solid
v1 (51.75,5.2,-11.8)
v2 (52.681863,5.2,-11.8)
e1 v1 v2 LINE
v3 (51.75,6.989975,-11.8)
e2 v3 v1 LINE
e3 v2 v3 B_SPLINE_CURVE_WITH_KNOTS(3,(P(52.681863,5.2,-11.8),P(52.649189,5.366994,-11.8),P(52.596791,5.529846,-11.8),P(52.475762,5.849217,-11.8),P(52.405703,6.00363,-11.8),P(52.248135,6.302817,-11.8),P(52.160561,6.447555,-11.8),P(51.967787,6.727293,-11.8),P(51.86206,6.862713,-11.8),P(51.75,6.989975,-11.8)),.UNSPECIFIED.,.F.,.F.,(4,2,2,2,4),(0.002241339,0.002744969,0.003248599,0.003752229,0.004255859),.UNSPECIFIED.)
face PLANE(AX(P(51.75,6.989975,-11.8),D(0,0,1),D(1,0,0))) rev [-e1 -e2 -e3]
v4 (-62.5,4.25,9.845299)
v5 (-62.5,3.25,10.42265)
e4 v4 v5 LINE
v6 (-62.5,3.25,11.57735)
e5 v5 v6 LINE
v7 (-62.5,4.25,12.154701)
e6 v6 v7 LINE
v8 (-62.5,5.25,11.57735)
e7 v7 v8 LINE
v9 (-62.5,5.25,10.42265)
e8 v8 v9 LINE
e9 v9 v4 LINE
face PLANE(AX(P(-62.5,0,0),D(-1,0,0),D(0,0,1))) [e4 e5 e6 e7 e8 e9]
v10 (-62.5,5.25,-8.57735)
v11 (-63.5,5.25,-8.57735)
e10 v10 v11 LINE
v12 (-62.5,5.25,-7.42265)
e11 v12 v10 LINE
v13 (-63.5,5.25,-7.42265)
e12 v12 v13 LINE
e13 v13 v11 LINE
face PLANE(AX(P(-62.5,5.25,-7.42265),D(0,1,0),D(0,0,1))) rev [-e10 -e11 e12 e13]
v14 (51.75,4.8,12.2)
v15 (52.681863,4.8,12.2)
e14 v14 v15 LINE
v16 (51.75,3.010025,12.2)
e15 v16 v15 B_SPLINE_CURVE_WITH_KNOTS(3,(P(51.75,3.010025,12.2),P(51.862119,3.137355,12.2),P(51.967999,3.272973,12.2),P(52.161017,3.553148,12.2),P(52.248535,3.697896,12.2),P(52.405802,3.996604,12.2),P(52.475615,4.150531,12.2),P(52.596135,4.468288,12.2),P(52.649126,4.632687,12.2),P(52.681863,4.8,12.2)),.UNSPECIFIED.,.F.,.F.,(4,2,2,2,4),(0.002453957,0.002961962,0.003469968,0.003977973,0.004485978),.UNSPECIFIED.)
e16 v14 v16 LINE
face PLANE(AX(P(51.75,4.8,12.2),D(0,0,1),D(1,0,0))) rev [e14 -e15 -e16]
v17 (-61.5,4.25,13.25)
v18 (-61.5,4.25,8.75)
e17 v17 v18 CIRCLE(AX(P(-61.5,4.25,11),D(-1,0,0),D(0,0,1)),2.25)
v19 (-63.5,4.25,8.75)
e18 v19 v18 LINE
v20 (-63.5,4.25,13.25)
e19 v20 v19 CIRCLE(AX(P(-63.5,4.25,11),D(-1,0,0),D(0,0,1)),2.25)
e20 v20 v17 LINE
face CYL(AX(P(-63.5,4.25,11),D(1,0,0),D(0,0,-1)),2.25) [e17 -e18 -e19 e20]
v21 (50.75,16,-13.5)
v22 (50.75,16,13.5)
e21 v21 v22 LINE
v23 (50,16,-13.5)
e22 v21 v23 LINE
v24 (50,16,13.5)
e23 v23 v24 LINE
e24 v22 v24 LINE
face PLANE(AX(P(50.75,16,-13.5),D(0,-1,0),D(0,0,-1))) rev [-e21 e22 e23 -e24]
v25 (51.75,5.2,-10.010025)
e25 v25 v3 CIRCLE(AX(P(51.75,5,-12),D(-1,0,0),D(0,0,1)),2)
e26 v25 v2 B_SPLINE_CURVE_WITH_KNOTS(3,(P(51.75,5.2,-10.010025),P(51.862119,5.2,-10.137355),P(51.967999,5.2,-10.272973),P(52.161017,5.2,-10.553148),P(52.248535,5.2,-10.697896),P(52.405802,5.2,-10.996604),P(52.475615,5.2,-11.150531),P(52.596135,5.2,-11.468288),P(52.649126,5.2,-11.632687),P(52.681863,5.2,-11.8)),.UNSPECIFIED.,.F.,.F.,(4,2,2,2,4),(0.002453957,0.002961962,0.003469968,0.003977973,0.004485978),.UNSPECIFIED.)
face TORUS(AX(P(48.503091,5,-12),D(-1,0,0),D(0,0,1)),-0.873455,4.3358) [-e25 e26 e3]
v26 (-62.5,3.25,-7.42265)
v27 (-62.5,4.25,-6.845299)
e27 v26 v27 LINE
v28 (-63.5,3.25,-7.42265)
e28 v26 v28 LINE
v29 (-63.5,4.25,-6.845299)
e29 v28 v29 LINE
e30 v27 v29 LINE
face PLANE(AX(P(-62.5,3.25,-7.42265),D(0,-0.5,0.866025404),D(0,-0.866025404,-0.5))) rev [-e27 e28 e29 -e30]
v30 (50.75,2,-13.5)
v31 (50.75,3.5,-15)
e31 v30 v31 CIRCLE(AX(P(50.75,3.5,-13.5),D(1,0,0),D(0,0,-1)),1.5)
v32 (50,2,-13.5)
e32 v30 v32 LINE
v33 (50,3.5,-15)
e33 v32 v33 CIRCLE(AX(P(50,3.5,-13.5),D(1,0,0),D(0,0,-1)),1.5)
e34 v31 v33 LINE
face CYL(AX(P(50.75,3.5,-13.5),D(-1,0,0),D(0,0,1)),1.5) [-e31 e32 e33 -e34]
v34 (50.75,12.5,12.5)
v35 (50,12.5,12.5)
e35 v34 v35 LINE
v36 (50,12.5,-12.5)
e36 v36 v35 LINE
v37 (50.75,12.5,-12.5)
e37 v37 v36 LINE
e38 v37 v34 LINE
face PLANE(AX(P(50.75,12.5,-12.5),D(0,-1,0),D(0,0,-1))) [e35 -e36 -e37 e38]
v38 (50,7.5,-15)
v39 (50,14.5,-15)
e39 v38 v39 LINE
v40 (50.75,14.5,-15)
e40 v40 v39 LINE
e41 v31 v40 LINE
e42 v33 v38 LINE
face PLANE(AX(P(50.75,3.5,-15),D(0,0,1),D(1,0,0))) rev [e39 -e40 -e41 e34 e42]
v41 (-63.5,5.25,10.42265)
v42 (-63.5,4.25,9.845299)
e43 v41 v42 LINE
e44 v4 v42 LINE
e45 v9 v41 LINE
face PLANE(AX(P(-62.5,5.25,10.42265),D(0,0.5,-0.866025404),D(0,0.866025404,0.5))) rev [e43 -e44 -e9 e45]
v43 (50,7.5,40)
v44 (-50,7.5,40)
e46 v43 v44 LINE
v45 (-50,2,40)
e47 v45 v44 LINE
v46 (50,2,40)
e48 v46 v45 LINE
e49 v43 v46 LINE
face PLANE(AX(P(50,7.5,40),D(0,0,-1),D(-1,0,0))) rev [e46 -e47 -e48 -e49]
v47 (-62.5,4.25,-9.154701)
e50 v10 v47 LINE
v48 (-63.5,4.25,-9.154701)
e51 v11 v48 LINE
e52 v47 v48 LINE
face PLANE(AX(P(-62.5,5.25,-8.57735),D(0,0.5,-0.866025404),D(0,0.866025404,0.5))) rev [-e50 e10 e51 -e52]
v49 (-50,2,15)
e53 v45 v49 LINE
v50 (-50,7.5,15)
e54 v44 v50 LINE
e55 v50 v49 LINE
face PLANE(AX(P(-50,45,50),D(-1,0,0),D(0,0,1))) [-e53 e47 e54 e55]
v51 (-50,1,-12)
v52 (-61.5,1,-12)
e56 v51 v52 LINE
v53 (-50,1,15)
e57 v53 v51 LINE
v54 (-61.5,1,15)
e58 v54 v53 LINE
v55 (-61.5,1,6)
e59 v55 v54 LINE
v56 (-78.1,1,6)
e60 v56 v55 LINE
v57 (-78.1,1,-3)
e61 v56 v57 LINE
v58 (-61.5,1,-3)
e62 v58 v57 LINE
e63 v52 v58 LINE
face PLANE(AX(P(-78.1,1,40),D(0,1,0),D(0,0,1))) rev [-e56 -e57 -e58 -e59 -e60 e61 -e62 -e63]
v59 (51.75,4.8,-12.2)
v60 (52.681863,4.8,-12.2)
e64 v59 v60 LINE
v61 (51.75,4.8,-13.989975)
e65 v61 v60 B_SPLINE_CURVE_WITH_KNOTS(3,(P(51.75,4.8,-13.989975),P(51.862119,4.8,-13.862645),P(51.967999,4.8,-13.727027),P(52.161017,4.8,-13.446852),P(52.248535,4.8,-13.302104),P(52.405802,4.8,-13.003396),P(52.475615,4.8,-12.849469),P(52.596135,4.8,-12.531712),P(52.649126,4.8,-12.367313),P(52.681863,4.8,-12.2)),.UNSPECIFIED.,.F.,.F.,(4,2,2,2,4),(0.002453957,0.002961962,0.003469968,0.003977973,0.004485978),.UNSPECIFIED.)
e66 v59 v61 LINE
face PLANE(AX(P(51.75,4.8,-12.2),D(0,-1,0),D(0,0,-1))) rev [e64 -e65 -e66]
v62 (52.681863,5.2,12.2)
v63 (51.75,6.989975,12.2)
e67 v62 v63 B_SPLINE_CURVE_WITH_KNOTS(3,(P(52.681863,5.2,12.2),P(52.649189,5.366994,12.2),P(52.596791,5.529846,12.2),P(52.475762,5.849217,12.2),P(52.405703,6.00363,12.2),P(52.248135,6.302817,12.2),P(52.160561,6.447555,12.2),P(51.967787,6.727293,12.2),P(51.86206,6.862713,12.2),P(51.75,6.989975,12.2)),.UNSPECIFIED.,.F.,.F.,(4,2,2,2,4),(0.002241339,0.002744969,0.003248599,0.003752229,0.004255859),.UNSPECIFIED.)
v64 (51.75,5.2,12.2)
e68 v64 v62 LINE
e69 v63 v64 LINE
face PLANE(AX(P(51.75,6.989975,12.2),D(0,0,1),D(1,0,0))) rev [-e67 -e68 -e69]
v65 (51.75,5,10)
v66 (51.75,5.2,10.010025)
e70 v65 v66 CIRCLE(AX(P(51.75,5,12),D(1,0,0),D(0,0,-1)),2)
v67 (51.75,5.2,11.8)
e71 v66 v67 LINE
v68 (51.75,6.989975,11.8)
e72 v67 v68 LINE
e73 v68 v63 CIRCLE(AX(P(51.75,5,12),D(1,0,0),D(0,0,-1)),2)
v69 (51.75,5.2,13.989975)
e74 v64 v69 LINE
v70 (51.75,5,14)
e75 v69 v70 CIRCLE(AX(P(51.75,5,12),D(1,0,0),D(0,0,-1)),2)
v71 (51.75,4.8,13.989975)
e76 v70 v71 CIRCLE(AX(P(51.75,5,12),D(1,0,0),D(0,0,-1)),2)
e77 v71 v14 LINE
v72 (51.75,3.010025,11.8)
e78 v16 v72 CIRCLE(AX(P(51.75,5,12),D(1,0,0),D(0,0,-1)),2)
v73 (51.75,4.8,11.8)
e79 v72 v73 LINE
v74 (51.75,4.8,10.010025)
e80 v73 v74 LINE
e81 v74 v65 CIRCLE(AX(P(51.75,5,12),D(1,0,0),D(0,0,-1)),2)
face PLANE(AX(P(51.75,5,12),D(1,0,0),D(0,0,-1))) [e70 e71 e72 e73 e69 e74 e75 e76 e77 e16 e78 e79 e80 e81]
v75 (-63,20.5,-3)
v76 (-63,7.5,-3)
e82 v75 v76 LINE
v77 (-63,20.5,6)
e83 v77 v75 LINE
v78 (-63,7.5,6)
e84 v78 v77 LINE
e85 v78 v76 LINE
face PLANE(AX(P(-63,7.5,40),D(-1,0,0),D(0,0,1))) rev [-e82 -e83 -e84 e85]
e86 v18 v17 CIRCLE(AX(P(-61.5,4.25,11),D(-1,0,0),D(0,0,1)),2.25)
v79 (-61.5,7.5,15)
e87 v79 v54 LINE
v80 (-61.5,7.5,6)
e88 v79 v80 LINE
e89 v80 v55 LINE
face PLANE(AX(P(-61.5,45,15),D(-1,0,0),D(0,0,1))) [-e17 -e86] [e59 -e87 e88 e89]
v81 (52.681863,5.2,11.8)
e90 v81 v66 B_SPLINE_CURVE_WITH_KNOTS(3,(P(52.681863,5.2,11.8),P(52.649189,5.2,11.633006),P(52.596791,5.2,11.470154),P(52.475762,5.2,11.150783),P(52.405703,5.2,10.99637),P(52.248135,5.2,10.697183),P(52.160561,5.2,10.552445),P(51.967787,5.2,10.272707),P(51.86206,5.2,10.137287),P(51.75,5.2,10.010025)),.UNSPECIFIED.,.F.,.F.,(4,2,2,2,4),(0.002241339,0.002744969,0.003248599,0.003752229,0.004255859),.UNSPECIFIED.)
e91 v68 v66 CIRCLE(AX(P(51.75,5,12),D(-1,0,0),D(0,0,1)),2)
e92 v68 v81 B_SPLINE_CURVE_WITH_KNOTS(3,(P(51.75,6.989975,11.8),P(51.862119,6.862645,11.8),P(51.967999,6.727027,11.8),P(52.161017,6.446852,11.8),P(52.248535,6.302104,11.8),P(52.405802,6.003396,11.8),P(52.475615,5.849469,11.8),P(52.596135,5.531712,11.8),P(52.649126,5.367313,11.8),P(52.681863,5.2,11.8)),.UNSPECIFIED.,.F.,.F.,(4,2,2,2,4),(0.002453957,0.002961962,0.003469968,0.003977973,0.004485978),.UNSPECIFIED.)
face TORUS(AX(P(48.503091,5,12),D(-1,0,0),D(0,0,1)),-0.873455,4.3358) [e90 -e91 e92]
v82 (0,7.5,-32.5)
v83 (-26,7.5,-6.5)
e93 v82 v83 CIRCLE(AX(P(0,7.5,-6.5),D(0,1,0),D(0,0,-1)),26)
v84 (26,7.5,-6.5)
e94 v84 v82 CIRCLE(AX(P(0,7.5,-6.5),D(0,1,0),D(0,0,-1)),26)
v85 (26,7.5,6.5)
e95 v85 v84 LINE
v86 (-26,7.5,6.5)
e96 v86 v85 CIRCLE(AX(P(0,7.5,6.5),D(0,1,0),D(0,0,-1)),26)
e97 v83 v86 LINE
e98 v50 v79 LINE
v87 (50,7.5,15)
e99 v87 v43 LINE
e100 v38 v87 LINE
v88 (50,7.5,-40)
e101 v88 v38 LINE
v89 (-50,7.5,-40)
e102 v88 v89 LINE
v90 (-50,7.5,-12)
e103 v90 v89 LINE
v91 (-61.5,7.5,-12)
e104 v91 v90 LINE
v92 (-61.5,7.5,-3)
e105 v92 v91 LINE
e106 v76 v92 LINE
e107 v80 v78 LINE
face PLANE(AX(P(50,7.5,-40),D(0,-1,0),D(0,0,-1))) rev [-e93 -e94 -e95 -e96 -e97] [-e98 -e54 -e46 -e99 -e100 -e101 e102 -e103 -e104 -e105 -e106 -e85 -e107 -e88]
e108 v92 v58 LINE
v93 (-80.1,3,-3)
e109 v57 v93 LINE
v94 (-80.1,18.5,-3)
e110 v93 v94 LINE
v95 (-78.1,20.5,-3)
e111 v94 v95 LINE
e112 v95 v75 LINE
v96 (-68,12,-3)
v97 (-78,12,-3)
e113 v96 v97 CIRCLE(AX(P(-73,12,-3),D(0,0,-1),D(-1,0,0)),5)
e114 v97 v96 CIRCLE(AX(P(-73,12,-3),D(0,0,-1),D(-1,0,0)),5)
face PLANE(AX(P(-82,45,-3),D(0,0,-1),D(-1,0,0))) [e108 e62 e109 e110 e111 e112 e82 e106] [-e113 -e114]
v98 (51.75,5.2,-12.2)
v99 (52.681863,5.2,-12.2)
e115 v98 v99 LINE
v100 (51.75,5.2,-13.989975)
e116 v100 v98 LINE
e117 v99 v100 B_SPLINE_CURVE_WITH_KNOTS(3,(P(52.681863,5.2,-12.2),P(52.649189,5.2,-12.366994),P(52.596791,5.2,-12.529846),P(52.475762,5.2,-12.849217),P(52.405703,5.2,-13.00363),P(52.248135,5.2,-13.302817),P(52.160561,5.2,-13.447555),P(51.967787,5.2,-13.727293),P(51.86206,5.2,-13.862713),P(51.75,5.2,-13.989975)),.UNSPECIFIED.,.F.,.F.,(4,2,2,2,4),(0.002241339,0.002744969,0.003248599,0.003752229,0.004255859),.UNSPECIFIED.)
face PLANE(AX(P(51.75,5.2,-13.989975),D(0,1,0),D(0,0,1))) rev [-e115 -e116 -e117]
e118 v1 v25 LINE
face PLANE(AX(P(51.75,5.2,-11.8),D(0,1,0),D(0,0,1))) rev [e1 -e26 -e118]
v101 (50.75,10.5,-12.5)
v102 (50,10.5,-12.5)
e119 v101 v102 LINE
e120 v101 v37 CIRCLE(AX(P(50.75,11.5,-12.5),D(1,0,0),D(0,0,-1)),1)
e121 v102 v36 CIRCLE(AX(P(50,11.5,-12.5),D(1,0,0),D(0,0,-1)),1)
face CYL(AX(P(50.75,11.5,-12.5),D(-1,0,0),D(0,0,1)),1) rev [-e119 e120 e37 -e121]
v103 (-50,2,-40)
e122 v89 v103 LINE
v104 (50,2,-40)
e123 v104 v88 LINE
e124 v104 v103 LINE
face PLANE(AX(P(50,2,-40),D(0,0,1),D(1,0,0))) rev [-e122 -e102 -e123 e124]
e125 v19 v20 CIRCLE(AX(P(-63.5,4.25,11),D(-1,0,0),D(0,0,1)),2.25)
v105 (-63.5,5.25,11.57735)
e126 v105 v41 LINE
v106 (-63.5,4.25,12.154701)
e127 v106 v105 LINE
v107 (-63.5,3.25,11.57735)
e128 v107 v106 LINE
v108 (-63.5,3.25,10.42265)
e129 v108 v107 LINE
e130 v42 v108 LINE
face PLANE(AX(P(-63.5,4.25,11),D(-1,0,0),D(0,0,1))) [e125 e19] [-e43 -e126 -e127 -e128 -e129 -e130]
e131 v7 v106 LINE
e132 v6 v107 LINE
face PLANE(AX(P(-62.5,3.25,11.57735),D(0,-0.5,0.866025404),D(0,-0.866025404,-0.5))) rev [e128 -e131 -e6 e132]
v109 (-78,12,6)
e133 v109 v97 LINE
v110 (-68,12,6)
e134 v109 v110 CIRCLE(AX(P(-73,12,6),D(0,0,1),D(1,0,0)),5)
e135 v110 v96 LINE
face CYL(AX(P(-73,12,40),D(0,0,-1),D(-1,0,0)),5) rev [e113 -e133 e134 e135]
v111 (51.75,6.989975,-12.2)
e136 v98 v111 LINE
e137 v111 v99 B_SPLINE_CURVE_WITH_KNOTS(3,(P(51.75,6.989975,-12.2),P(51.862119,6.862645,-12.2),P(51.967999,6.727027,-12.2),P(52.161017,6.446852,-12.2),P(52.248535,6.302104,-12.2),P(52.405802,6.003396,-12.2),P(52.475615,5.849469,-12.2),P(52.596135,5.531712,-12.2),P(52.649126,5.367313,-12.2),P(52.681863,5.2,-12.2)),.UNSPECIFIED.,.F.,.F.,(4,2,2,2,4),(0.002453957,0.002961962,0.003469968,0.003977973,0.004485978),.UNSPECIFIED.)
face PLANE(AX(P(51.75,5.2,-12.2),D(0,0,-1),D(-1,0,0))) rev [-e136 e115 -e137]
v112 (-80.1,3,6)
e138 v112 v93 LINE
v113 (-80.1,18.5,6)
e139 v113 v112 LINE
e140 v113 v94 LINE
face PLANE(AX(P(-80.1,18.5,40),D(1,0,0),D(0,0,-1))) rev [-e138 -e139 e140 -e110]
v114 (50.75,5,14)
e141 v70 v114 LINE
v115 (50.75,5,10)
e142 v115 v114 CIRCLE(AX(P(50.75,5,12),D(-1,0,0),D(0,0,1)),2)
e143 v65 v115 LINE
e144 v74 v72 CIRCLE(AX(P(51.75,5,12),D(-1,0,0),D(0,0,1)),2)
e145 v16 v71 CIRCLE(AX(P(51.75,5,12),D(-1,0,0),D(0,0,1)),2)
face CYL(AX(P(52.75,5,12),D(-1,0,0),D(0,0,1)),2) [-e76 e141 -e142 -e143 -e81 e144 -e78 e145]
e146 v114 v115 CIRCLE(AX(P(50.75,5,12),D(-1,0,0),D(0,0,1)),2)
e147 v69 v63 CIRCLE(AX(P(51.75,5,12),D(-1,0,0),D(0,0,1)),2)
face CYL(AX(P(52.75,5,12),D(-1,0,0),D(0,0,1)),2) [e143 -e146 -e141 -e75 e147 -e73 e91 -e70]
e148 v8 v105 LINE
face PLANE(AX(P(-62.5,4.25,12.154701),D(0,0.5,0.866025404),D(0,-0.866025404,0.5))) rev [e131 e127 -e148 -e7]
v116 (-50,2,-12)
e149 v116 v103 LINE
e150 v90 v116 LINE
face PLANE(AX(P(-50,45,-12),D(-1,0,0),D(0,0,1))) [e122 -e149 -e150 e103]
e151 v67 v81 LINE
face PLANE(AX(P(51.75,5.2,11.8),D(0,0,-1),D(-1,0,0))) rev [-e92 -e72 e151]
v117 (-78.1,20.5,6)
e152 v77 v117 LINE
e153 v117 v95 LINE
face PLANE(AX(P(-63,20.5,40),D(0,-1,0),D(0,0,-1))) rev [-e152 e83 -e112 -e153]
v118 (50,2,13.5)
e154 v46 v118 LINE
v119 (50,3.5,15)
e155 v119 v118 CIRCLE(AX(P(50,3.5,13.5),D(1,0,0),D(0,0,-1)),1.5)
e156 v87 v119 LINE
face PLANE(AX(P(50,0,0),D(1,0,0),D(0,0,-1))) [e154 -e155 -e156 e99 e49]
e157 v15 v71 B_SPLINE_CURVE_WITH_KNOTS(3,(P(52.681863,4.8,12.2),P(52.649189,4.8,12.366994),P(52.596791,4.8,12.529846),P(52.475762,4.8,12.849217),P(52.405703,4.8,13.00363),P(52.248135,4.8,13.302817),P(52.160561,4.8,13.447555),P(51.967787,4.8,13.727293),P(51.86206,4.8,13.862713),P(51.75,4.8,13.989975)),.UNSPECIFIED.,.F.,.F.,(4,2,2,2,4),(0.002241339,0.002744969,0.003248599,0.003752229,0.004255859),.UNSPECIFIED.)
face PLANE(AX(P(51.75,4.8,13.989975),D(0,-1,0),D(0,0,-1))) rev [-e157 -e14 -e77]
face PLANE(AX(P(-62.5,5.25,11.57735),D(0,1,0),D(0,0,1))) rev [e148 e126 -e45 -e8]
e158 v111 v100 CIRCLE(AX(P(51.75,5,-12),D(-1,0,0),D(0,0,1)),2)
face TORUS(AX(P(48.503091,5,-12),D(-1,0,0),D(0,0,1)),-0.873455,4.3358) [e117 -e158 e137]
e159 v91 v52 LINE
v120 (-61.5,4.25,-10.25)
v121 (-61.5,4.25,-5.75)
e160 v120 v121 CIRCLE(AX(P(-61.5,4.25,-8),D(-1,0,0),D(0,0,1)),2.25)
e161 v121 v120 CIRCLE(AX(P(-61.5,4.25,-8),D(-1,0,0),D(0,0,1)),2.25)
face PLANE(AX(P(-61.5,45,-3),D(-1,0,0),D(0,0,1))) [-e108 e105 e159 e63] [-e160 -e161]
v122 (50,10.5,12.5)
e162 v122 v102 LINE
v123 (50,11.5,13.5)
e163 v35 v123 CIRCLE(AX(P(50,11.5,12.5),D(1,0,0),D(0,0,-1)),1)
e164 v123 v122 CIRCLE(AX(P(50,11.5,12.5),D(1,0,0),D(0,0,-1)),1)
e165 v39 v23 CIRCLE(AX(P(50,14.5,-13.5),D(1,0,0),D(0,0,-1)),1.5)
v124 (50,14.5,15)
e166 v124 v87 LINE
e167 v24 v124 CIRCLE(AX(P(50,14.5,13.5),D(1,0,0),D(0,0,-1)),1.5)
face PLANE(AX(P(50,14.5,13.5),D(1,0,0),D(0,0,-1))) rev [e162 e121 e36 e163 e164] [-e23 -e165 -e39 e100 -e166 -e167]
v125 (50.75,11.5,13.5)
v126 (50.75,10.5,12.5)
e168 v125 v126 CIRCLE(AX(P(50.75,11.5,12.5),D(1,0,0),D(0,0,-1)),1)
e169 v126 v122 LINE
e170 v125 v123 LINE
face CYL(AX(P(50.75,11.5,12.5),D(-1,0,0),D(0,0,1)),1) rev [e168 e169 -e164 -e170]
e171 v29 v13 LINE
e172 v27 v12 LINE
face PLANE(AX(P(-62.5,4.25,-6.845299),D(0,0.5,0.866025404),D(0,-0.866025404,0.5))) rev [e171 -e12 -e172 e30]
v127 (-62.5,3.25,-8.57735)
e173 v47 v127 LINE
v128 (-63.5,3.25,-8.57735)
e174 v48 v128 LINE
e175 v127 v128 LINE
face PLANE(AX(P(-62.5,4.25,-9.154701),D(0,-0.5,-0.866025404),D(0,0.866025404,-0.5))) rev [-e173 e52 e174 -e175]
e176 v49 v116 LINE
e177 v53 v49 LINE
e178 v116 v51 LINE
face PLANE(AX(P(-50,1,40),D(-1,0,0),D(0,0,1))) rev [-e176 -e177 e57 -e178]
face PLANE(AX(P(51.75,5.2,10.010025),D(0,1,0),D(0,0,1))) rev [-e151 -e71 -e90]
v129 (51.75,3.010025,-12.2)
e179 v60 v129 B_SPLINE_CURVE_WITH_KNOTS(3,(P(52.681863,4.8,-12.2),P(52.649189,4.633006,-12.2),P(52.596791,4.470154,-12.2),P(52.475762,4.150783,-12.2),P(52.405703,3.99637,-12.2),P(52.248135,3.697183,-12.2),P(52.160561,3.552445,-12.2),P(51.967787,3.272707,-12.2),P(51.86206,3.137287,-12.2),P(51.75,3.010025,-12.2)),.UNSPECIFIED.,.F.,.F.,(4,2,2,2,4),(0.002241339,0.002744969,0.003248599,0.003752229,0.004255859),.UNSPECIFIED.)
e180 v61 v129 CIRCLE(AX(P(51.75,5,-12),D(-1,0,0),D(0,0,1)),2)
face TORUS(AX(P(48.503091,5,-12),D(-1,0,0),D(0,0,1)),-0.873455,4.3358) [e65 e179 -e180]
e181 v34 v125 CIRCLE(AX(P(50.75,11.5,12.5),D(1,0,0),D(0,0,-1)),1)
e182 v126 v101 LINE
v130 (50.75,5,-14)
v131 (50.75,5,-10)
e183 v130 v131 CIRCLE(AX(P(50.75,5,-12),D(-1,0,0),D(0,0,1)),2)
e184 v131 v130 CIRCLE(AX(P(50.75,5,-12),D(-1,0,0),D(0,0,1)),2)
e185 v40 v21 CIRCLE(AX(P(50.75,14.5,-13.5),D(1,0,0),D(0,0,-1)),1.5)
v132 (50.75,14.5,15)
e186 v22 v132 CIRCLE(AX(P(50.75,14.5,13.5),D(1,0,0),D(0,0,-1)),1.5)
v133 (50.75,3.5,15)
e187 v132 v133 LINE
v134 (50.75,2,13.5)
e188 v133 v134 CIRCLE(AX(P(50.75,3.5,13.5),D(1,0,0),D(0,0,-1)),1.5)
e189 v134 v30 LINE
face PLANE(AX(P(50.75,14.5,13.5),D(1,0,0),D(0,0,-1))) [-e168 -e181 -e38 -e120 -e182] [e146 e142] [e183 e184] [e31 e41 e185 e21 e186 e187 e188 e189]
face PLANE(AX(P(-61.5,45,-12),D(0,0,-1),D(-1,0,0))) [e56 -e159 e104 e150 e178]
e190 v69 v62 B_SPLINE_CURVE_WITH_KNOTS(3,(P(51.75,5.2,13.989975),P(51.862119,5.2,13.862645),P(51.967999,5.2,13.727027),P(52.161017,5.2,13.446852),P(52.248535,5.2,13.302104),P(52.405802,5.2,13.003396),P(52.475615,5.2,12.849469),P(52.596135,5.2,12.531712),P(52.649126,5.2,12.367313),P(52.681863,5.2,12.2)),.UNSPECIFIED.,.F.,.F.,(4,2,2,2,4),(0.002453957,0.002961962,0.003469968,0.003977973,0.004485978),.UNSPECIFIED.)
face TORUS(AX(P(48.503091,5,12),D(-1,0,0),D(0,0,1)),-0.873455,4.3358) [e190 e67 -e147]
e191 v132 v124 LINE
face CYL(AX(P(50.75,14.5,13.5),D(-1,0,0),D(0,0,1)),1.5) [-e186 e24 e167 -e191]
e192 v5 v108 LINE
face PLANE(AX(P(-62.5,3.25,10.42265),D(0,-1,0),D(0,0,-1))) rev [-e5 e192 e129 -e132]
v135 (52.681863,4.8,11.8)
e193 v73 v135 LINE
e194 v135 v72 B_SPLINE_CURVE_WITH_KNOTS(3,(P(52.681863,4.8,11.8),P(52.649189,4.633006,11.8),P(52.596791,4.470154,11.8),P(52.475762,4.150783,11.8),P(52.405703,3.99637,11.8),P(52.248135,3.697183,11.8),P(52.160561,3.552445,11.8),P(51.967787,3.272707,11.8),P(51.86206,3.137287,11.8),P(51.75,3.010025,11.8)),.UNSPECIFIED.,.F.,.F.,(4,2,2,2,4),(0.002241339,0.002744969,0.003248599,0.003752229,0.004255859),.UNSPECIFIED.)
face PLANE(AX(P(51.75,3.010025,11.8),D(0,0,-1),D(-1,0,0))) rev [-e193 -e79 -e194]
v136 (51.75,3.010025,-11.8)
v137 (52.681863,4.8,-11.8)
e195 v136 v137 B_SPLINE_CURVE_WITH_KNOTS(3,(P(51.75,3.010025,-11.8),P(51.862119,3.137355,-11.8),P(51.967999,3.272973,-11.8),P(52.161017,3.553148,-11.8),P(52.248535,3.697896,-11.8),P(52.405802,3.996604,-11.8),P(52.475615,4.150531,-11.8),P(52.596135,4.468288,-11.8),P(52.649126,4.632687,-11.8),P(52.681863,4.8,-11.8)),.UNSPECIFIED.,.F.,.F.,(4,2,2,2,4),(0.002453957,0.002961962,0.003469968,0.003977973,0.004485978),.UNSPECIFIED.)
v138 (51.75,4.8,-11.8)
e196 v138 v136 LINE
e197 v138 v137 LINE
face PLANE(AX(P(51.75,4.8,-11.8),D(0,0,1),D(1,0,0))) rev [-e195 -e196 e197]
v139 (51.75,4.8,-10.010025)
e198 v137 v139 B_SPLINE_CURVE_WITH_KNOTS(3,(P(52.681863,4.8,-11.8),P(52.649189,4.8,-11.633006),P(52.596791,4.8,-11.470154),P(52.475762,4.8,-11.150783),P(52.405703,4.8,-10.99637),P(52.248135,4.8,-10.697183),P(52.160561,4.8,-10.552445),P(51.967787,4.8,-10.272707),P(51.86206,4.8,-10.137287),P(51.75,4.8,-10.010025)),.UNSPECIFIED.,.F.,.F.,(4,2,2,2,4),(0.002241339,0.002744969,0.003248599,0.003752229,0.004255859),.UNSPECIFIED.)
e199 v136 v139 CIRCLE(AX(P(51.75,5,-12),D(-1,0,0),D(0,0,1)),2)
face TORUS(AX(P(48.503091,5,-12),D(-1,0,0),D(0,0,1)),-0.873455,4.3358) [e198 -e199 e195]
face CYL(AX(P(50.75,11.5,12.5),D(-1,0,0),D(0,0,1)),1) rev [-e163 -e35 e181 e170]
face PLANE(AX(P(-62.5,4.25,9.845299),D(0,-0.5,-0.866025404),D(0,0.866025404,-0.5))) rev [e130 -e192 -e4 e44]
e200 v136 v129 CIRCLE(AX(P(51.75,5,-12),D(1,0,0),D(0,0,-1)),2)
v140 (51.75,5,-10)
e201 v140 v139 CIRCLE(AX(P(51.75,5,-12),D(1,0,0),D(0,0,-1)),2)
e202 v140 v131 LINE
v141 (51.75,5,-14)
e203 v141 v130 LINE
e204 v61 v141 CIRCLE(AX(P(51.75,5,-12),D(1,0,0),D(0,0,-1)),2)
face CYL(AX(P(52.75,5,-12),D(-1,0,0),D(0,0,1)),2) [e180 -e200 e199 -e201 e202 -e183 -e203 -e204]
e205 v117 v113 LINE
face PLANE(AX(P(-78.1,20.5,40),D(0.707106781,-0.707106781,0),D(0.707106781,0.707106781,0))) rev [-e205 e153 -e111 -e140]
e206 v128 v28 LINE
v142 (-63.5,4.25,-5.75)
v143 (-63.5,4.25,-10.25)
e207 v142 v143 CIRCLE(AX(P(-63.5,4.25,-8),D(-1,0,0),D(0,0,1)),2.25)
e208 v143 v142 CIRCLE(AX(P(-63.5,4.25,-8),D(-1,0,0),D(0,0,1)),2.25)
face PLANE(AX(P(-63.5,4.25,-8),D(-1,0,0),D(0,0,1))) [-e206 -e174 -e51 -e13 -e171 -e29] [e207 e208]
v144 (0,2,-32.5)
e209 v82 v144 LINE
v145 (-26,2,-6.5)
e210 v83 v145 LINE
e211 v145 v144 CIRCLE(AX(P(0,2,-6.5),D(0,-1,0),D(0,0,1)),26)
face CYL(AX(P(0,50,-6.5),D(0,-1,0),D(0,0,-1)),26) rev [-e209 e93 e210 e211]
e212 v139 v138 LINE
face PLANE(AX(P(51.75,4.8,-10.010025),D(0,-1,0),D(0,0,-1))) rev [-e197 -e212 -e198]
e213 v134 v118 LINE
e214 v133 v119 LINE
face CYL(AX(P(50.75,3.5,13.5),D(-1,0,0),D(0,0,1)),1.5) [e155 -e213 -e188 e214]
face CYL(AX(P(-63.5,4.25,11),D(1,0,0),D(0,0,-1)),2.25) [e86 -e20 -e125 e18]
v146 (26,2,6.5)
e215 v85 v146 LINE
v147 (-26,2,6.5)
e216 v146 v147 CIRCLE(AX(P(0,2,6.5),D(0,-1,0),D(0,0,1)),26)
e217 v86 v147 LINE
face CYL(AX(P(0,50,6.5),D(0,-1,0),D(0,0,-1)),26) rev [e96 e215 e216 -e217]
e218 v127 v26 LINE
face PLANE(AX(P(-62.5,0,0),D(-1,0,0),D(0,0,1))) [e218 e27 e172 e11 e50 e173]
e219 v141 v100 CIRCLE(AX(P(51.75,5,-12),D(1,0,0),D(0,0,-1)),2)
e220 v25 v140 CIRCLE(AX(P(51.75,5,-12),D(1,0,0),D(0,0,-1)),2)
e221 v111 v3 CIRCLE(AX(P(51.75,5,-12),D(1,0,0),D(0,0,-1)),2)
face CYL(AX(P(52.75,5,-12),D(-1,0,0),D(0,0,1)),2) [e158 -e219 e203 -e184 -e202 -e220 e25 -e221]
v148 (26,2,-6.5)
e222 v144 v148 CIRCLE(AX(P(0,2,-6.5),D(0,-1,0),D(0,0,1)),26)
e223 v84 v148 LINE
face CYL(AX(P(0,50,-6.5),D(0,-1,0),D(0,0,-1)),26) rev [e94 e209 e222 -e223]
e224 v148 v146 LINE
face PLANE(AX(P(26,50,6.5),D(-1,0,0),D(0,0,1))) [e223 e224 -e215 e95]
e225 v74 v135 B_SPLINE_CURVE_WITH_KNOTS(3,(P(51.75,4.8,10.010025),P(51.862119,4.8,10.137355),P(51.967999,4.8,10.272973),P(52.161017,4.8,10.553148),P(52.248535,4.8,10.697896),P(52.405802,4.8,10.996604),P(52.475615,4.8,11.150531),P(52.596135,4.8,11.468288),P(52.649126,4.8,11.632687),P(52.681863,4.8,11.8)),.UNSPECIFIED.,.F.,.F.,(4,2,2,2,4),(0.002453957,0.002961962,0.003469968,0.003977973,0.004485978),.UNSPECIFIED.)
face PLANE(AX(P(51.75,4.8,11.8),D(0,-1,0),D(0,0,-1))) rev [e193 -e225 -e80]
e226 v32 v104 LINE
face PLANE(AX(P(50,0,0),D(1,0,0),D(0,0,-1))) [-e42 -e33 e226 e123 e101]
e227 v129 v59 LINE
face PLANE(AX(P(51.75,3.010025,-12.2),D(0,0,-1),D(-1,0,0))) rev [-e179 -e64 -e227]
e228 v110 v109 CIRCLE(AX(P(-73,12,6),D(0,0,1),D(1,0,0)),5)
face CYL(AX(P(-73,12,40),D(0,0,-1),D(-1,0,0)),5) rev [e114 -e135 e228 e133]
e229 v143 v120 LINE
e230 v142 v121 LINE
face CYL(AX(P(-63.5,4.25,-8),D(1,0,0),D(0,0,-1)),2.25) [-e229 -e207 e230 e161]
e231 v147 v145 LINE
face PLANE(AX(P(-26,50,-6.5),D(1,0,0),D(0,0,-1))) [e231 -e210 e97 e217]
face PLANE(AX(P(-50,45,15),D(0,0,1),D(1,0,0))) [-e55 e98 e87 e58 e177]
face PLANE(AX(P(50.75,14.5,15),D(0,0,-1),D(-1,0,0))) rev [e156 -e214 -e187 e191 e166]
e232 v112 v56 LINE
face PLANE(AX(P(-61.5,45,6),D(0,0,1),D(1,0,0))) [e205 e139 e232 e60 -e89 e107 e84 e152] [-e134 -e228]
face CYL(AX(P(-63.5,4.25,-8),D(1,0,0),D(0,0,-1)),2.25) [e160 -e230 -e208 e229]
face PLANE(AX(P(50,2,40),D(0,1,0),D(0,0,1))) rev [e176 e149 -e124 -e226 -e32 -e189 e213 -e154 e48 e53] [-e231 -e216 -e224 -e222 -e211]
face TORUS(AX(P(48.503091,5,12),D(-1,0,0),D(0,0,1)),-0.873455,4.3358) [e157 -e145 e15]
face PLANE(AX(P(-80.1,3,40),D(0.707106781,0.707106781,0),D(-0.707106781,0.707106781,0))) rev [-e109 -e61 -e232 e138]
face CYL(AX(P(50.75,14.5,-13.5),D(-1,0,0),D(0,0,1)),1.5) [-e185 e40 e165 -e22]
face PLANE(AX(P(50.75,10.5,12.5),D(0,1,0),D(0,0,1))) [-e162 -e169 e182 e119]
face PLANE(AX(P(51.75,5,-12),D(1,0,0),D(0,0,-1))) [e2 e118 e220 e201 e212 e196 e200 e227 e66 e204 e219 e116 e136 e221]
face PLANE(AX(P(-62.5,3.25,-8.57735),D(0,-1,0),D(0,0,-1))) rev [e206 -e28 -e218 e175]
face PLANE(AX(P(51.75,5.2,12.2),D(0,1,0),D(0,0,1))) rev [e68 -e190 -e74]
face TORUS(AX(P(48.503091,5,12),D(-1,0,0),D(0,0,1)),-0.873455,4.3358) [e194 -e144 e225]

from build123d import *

# Parameters (mm, degrees)
EXTRUDE_1_DEPTH      = 50
EXTRUDE_1_DEPTH_BACK = 50
SKETCH_1_W           = 80
SKETCH_1_H           = 5.5
EXTRUDE_2_DEPTH      = 40
EXTRUDE_2_DEPTH_BACK = 40
SKETCH_2_R           = 5
CUT_EXTRUDE_1_DEPTH  = 45
EXTRUDE_3_DEPTH      = 0.75
CUT_EXTRUDE_2_DEPTH  = 1
CUT_EXTRUDE_3_DEPTH  = 1
CUT_EXTRUDE_4_DEPTH  = 50
SKETCH_10_R          = 2.25
EXTRUDE_4_DEPTH      = 2
SKETCH_11_R          = 2.25
EXTRUDE_5_DEPTH      = 2
CUT_EXTRUDE_5_DEPTH  = 1
CUT_EXTRUDE_6_DEPTH  = 1


with BuildPart() as part:
    # 草图1 → 凸台-拉伸1 (new, two sides: drawn at the far end of the back side and taken through both)
    with BuildSketch(Plane(origin=(0, 0, 0), x_dir=(0, 0, -1), z_dir=(1, 0, 0)).offset(-EXTRUDE_1_DEPTH_BACK)):
        with Locations((0, 4.75)):
            Rectangle(SKETCH_1_W, SKETCH_1_H)
    extrude(amount=EXTRUDE_1_DEPTH + EXTRUDE_1_DEPTH_BACK)

    # 草图2 → 凸台-拉伸2 (add, two sides: drawn at the far end of the back side and taken through both)
    with BuildSketch(Plane.XY.offset(-EXTRUDE_2_DEPTH_BACK)):
        Polygon((-80.1, 18.5), (-80.1, 3), (-78.1, 1), (-50, 1), (-50, 7.5), (-63, 7.5), (-63, 20.5), (-78.1, 20.5), align=None)
        with Locations((-73, 12)):
            Circle(SKETCH_2_R, mode=Mode.SUBTRACT)
    extrude(amount=EXTRUDE_2_DEPTH + EXTRUDE_2_DEPTH_BACK)

    # 草图3 → 切除-拉伸1 (cut)
    with BuildSketch(Plane(origin=(0, 0, 0), x_dir=(-1, 0, 0), z_dir=(0, 1, 0))):
        Polygon((84.5, -50), (84.5, 50), (50, 50), (50, 15), (61.5, 15), (61.5, 6), (82, 6), (82, -3), (61.5, -3), (61.5, -12), (50, -12), (50, -50), align=None)
    extrude(amount=CUT_EXTRUDE_1_DEPTH, mode=Mode.SUBTRACT)

    # 草图4 → 凸台-拉伸3 (add)
    with BuildSketch(Plane(origin=(50, 0, 0), x_dir=(0, 0, -1), z_dir=(1, 0, 0))):
        with BuildLine():
            Line((-15, 14.5), (-15, 3.5))
            ThreePointArc((-15, 3.5), (-14.560660172, 2.439339828), (-13.5, 2))
            Line((-13.5, 2), (13.5, 2))
            ThreePointArc((13.5, 2), (14.560660172, 2.439339828), (15, 3.5))
            Line((15, 3.5), (15, 14.5))
            ThreePointArc((15, 14.5), (14.560660172, 15.560660172), (13.5, 16))
            Line((13.5, 16), (-13.5, 16))
            ThreePointArc((-13.5, 16), (-14.560660172, 15.560660172), (-15, 14.5))
        make_face()
        with BuildLine():
            Line((-12.5, 10.5), (12.5, 10.5))
            ThreePointArc((12.5, 10.5), (13.5, 11.5), (12.5, 12.5))
            Line((12.5, 12.5), (-12.5, 12.5))
            ThreePointArc((-12.5, 12.5), (-13.5, 11.5), (-12.5, 10.5))
        make_face(mode=Mode.SUBTRACT)
    extrude(amount=EXTRUDE_3_DEPTH)

    # 草图5 → 旋转1 (revolve)
    with BuildSketch(Plane.XY.offset(12), mode=Mode.PRIVATE) as revolve_1_sk:
        with BuildLine():
            Line((50.75, 5), (50.75, 7))
            Line((50.75, 7), (51.75, 7))
            ThreePointArc((51.75, 7), (52.381148113, 6.065574057), (52.75, 5))
            Line((52.75, 5), (50.75, 5))
        make_face()
    revolve(revolve_1_sk.sketch.rotate(Axis((52.75, 5, 12), (-1, 0, 0)), 270), axis=Axis((52.75, 5, 12), (-1, 0, 0)))

    # 草图6 → 旋转2 (revolve)
    with BuildSketch(Plane.XY.offset(-12), mode=Mode.PRIVATE) as revolve_2_sk:
        with BuildLine():
            Line((50.75, 5), (50.75, 7))
            Line((50.75, 7), (51.75, 7))
            ThreePointArc((51.75, 7), (52.381148113, 6.065574057), (52.75, 5))
            Line((52.75, 5), (50.75, 5))
        make_face()
    revolve(revolve_2_sk.sketch.rotate(Axis((52.75, 5, -12), (-1, 0, 0)), 270), axis=Axis((52.75, 5, -12), (-1, 0, 0)))

    # 草图7 → 切除-拉伸2 (cut)
    with BuildSketch(Plane(origin=(52.75, 0, 0), x_dir=(0, 0, -1), z_dir=(1, 0, 0))):
        with BuildLine():
            Line((10.010025126, 4.8), (11.8, 4.8))
            Line((11.8, 4.8), (11.8, 3.010025126))
            ThreePointArc((11.8, 3.010025126), (12, 3), (12.2, 3.010025126))
            Line((12.2, 3.010025126), (12.2, 4.8))
            Line((12.2, 4.8), (13.989974874, 4.8))
            ThreePointArc((13.989974874, 4.8), (14, 5), (13.989974874, 5.2))
            Line((13.989974874, 5.2), (12.2, 5.2))
            Line((12.2, 5.2), (12.2, 6.989974874))
            ThreePointArc((12.2, 6.989974874), (12, 7), (11.8, 6.989974874))
            Line((11.8, 6.989974874), (11.8, 5.2))
            Line((11.8, 5.2), (10.010025126, 5.2))
            ThreePointArc((10.010025126, 5.2), (10, 5), (10.010025126, 4.8))
        make_face()
    extrude(amount=-CUT_EXTRUDE_2_DEPTH, mode=Mode.SUBTRACT)

    # 草图8 → 切除-拉伸3 (cut)
    with BuildSketch(Plane(origin=(52.75, 0, 0), x_dir=(0, 0, -1), z_dir=(1, 0, 0))):
        with BuildLine():
            Line((-13.989974874, 4.8), (-12.2, 4.8))
            Line((-12.2, 4.8), (-12.2, 3.010025126))
            ThreePointArc((-12.2, 3.010025126), (-12, 3), (-11.8, 3.010025126))
            Line((-11.8, 3.010025126), (-11.8, 4.8))
            Line((-11.8, 4.8), (-10.010025126, 4.8))
            ThreePointArc((-10.010025126, 4.8), (-10, 5), (-10.010025126, 5.2))
            Line((-10.010025126, 5.2), (-11.8, 5.2))
            Line((-11.8, 5.2), (-11.8, 6.989974874))
            ThreePointArc((-11.8, 6.989974874), (-12, 7), (-12.2, 6.989974874))
            Line((-12.2, 6.989974874), (-12.2, 5.2))
            Line((-12.2, 5.2), (-13.989974874, 5.2))
            ThreePointArc((-13.989974874, 5.2), (-14, 5), (-13.989974874, 4.8))
        make_face()
    extrude(amount=-CUT_EXTRUDE_3_DEPTH, mode=Mode.SUBTRACT)

    # 草图9 → 切除-拉伸4 (cut)
    with BuildSketch(Plane(origin=(0, 0, 0), x_dir=(-1, 0, 0), z_dir=(0, 1, 0))):
        with BuildLine():
            Line((-26, 6.5), (-26, -6.5))
            ThreePointArc((-26, -6.5), (0, -32.5), (26, -6.5))
            Line((26, -6.5), (26, 6.5))
            ThreePointArc((26, 6.5), (0, 32.5), (-26, 6.5))
        make_face()
    extrude(amount=CUT_EXTRUDE_4_DEPTH, mode=Mode.SUBTRACT)

    # 草图10 → 凸台-拉伸4 (add)
    with BuildSketch(Plane.ZY.offset(61.5)):
        with Locations((-8, 4.25)):
            Circle(SKETCH_10_R)
    extrude(amount=EXTRUDE_4_DEPTH)

    # 草图11 → 凸台-拉伸5 (add)
    with BuildSketch(Plane.ZY.offset(61.5)):
        with Locations((11, 4.25)):
            Circle(SKETCH_11_R)
    extrude(amount=EXTRUDE_5_DEPTH)

    # 草图12 → 切除-拉伸5 (cut)
    with BuildSketch(Plane.ZY.offset(63.5)):
        Polygon((-7.422649731, 3.25), (-6.845299462, 4.25), (-7.422649731, 5.25), (-8.577350269, 5.25), (-9.154700538, 4.25), (-8.577350269, 3.25), align=None)
    extrude(amount=-CUT_EXTRUDE_5_DEPTH, mode=Mode.SUBTRACT)

    # 草图13 → 切除-拉伸6 (cut)
    with BuildSketch(Plane.ZY.offset(63.5)):
        Polygon((11.577350269, 3.25), (12.154700538, 4.25), (11.577350269, 5.25), (10.422649731, 5.25), (9.845299462, 4.25), (10.422649731, 3.25), align=None)
    extrude(amount=-CUT_EXTRUDE_6_DEPTH, mode=Mode.SUBTRACT)


solid = part.part
